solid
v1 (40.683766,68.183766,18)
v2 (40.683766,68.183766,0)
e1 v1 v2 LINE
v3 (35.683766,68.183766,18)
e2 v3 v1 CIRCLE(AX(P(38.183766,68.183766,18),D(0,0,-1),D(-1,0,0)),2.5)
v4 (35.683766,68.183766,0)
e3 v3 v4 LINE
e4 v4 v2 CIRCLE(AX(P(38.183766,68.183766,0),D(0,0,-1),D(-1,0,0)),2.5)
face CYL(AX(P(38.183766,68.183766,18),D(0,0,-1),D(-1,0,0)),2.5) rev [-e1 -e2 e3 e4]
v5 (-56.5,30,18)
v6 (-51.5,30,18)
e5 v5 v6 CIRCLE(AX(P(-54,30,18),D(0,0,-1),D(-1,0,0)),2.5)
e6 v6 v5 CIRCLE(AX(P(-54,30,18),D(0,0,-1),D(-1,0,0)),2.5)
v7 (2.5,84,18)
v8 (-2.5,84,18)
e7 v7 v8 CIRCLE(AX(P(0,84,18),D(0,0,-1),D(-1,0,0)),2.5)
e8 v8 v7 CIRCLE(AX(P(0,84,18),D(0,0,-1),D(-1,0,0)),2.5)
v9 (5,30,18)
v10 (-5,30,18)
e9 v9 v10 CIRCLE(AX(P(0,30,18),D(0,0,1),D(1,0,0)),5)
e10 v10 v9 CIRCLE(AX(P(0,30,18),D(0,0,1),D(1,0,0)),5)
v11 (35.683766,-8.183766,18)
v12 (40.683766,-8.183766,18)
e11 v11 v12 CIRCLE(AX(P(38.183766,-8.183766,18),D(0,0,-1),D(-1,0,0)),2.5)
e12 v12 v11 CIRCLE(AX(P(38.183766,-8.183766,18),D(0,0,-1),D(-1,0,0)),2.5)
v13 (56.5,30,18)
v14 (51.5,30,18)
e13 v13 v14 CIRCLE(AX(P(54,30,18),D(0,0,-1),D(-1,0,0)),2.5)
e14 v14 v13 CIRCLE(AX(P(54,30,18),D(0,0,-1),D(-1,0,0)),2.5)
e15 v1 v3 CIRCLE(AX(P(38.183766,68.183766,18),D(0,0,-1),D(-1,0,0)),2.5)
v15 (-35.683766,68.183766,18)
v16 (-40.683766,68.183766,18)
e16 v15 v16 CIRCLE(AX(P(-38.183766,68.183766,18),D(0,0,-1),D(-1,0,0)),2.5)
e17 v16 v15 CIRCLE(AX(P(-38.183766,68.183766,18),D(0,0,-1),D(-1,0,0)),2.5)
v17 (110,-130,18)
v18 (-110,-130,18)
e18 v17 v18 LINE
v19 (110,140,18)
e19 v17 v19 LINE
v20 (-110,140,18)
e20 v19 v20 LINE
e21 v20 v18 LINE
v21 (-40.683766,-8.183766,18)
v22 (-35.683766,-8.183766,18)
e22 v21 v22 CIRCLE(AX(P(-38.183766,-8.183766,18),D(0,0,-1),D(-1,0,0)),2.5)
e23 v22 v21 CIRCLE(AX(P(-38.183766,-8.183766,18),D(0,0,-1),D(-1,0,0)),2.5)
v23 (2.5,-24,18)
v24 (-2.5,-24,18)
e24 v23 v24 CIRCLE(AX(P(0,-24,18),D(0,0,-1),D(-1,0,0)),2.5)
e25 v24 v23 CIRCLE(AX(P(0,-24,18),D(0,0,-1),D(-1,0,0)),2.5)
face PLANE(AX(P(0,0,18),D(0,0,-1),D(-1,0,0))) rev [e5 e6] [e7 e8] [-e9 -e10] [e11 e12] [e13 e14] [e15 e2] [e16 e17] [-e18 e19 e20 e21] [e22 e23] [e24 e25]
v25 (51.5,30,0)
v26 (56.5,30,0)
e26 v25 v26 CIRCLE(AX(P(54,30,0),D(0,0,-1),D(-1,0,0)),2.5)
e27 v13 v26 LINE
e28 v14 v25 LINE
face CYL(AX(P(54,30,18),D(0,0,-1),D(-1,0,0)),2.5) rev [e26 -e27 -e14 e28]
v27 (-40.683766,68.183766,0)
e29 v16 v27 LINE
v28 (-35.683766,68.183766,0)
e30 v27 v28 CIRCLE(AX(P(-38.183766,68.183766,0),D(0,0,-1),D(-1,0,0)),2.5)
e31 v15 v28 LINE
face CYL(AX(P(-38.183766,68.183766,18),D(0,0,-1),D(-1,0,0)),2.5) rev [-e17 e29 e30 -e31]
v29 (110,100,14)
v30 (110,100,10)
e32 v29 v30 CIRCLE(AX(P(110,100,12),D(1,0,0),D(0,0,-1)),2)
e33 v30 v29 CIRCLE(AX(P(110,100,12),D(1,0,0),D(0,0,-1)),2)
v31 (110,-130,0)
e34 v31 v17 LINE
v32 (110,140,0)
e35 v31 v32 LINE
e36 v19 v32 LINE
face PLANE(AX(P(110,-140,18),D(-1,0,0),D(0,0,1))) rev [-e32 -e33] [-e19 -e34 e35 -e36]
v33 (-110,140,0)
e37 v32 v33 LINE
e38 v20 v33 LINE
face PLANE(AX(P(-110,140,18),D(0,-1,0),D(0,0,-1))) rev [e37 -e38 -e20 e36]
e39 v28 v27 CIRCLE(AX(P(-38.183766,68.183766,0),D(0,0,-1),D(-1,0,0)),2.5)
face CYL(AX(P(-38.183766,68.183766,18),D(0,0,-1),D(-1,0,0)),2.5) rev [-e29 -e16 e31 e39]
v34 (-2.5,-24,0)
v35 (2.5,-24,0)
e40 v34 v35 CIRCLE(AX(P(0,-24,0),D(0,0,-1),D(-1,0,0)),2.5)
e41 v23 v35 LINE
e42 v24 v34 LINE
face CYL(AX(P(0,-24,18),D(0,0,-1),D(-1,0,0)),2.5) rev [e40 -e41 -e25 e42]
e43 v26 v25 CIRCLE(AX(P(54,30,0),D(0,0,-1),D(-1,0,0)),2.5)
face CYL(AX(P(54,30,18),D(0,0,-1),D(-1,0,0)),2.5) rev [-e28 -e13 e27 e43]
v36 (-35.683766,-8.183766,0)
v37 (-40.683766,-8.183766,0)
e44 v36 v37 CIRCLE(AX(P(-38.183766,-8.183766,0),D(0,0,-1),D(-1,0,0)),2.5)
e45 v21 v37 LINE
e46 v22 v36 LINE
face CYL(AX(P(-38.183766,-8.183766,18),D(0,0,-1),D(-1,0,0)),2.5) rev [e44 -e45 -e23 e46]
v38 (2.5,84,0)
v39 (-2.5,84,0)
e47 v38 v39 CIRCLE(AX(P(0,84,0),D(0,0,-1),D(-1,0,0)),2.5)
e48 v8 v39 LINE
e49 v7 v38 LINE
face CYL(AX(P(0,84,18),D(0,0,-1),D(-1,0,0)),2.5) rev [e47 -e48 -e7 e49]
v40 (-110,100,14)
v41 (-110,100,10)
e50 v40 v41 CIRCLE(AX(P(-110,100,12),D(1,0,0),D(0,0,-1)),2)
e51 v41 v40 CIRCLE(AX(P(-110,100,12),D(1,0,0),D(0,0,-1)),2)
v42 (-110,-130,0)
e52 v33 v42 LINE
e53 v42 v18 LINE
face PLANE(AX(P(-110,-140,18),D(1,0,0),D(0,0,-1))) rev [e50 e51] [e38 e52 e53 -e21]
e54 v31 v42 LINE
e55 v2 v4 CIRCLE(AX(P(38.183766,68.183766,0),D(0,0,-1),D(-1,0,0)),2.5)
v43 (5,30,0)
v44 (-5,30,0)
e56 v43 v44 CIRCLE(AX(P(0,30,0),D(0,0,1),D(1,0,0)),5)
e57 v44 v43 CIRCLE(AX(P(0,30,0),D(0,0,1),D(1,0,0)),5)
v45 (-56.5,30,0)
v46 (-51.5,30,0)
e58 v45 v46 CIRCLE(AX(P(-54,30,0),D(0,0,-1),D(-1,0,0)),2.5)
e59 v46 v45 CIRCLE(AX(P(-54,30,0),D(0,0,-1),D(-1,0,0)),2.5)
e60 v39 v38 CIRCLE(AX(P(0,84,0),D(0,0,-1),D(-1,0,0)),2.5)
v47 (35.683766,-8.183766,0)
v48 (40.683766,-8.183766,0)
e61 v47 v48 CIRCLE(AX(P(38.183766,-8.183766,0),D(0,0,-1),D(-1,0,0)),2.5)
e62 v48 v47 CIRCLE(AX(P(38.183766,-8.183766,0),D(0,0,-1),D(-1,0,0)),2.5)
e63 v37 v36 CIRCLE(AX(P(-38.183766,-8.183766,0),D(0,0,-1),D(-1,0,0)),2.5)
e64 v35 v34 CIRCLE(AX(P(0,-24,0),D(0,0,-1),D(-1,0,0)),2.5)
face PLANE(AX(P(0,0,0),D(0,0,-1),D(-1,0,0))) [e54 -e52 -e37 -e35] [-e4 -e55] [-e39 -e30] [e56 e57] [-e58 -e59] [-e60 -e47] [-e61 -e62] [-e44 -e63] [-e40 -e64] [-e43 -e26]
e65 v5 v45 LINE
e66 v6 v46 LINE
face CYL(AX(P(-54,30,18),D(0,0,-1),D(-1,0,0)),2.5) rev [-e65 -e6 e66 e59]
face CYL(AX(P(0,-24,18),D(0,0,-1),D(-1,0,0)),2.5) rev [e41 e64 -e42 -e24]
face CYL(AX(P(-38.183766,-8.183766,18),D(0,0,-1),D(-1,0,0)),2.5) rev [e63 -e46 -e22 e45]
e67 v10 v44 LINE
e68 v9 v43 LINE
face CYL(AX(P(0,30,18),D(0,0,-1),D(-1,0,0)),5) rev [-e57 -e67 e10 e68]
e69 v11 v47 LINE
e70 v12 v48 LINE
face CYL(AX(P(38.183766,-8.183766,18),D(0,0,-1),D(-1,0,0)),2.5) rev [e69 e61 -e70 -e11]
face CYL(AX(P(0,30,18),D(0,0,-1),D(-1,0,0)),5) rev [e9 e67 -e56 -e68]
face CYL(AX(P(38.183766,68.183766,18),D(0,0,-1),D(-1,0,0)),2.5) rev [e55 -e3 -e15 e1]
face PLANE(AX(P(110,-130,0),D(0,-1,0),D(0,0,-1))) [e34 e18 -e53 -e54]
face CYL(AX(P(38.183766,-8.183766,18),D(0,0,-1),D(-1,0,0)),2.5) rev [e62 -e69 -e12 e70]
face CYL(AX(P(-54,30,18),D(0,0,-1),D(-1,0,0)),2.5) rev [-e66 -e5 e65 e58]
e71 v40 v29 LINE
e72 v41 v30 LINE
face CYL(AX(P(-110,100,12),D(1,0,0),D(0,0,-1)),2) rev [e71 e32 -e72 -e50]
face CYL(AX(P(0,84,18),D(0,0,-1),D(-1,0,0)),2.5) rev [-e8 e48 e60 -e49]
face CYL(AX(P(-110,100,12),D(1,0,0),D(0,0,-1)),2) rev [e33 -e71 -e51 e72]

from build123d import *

# Parameters (mm, degrees)
SKETCH_1_W          = 220
SKETCH_1_H          = 280
EXTRUDE_1_DEPTH     = 18
SKETCH_2_W          = 220
SKETCH_2_H          = 60
CUT_EXTRUDE_1_DEPTH = 179.952507666
SKETCH_4_R          = 5
CUT_EXTRUDE_3_DEPTH = 179.952507666
SKETCH_5_R          = 2.5
CUT_EXTRUDE_4_DEPTH = 179.952507666
SKETCH_13_W         = 18
SKETCH_13_H         = 50
EXTRUDE_2_DEPTH     = 220
SKETCH_15_R         = 2
CUT_EXTRUDE_5_DEPTH = 262.388599598


with BuildPart() as part:
    # 草图1 → 凸台-拉伸1 (new body)
    with BuildSketch(Plane.XY):
        Rectangle(SKETCH_1_W, SKETCH_1_H)
    extrude(amount=EXTRUDE_1_DEPTH)

    # 草图2 → 切除-拉伸1 (cut, through all)
    with BuildSketch(Plane.XY):
        with Locations((0, -110)):
            Rectangle(SKETCH_2_W, SKETCH_2_H)
    extrude(amount=CUT_EXTRUDE_1_DEPTH, mode=Mode.SUBTRACT)

    # 草图4 → 切除-拉伸3 (cut, through all)
    with BuildSketch(Plane.XY):
        with Locations((0, 30)):
            Circle(SKETCH_4_R)
    extrude(amount=CUT_EXTRUDE_3_DEPTH, mode=Mode.SUBTRACT)

    # 草图5 → 切除-拉伸4 (cut, through all)
    with BuildSketch(Plane(origin=(0, 0, 0), x_dir=(-1, 0, 0), z_dir=(0, 0, -1))):
        with Locations((-38.183766184, 68.183766184)):
            Circle(SKETCH_5_R)
        with Locations((0, 84)):
            Circle(SKETCH_5_R)
        with Locations((-54, 30)):
            Circle(SKETCH_5_R)
        with Locations((-38.183766184, -8.183766184)):
            Circle(SKETCH_5_R)
        with Locations((0, -24)):
            Circle(SKETCH_5_R)
        with Locations((38.183766184, -8.183766184)):
            Circle(SKETCH_5_R)
        with Locations((54, 30)):
            Circle(SKETCH_5_R)
        with Locations((38.183766184, 68.183766184)):
            Circle(SKETCH_5_R)
    extrude(amount=-CUT_EXTRUDE_4_DEPTH, mode=Mode.SUBTRACT)

    # 草图13 → 凸台-拉伸2 (add, through all)
    with BuildSketch(Plane.ZY.offset(110)):
        with Locations((9, -105)):
            Rectangle(SKETCH_13_W, SKETCH_13_H)
    extrude(amount=-EXTRUDE_2_DEPTH)

    # 草图15 → 切除-拉伸5 (cut, through all)
    with BuildSketch(Plane(origin=(110, 0, 0), x_dir=(0, 0, -1), z_dir=(1, 0, 0))):
        with Locations((-12, 100)):
            Circle(SKETCH_15_R)
    extrude(amount=-CUT_EXTRUDE_5_DEPTH, mode=Mode.SUBTRACT)


solid = part.part
